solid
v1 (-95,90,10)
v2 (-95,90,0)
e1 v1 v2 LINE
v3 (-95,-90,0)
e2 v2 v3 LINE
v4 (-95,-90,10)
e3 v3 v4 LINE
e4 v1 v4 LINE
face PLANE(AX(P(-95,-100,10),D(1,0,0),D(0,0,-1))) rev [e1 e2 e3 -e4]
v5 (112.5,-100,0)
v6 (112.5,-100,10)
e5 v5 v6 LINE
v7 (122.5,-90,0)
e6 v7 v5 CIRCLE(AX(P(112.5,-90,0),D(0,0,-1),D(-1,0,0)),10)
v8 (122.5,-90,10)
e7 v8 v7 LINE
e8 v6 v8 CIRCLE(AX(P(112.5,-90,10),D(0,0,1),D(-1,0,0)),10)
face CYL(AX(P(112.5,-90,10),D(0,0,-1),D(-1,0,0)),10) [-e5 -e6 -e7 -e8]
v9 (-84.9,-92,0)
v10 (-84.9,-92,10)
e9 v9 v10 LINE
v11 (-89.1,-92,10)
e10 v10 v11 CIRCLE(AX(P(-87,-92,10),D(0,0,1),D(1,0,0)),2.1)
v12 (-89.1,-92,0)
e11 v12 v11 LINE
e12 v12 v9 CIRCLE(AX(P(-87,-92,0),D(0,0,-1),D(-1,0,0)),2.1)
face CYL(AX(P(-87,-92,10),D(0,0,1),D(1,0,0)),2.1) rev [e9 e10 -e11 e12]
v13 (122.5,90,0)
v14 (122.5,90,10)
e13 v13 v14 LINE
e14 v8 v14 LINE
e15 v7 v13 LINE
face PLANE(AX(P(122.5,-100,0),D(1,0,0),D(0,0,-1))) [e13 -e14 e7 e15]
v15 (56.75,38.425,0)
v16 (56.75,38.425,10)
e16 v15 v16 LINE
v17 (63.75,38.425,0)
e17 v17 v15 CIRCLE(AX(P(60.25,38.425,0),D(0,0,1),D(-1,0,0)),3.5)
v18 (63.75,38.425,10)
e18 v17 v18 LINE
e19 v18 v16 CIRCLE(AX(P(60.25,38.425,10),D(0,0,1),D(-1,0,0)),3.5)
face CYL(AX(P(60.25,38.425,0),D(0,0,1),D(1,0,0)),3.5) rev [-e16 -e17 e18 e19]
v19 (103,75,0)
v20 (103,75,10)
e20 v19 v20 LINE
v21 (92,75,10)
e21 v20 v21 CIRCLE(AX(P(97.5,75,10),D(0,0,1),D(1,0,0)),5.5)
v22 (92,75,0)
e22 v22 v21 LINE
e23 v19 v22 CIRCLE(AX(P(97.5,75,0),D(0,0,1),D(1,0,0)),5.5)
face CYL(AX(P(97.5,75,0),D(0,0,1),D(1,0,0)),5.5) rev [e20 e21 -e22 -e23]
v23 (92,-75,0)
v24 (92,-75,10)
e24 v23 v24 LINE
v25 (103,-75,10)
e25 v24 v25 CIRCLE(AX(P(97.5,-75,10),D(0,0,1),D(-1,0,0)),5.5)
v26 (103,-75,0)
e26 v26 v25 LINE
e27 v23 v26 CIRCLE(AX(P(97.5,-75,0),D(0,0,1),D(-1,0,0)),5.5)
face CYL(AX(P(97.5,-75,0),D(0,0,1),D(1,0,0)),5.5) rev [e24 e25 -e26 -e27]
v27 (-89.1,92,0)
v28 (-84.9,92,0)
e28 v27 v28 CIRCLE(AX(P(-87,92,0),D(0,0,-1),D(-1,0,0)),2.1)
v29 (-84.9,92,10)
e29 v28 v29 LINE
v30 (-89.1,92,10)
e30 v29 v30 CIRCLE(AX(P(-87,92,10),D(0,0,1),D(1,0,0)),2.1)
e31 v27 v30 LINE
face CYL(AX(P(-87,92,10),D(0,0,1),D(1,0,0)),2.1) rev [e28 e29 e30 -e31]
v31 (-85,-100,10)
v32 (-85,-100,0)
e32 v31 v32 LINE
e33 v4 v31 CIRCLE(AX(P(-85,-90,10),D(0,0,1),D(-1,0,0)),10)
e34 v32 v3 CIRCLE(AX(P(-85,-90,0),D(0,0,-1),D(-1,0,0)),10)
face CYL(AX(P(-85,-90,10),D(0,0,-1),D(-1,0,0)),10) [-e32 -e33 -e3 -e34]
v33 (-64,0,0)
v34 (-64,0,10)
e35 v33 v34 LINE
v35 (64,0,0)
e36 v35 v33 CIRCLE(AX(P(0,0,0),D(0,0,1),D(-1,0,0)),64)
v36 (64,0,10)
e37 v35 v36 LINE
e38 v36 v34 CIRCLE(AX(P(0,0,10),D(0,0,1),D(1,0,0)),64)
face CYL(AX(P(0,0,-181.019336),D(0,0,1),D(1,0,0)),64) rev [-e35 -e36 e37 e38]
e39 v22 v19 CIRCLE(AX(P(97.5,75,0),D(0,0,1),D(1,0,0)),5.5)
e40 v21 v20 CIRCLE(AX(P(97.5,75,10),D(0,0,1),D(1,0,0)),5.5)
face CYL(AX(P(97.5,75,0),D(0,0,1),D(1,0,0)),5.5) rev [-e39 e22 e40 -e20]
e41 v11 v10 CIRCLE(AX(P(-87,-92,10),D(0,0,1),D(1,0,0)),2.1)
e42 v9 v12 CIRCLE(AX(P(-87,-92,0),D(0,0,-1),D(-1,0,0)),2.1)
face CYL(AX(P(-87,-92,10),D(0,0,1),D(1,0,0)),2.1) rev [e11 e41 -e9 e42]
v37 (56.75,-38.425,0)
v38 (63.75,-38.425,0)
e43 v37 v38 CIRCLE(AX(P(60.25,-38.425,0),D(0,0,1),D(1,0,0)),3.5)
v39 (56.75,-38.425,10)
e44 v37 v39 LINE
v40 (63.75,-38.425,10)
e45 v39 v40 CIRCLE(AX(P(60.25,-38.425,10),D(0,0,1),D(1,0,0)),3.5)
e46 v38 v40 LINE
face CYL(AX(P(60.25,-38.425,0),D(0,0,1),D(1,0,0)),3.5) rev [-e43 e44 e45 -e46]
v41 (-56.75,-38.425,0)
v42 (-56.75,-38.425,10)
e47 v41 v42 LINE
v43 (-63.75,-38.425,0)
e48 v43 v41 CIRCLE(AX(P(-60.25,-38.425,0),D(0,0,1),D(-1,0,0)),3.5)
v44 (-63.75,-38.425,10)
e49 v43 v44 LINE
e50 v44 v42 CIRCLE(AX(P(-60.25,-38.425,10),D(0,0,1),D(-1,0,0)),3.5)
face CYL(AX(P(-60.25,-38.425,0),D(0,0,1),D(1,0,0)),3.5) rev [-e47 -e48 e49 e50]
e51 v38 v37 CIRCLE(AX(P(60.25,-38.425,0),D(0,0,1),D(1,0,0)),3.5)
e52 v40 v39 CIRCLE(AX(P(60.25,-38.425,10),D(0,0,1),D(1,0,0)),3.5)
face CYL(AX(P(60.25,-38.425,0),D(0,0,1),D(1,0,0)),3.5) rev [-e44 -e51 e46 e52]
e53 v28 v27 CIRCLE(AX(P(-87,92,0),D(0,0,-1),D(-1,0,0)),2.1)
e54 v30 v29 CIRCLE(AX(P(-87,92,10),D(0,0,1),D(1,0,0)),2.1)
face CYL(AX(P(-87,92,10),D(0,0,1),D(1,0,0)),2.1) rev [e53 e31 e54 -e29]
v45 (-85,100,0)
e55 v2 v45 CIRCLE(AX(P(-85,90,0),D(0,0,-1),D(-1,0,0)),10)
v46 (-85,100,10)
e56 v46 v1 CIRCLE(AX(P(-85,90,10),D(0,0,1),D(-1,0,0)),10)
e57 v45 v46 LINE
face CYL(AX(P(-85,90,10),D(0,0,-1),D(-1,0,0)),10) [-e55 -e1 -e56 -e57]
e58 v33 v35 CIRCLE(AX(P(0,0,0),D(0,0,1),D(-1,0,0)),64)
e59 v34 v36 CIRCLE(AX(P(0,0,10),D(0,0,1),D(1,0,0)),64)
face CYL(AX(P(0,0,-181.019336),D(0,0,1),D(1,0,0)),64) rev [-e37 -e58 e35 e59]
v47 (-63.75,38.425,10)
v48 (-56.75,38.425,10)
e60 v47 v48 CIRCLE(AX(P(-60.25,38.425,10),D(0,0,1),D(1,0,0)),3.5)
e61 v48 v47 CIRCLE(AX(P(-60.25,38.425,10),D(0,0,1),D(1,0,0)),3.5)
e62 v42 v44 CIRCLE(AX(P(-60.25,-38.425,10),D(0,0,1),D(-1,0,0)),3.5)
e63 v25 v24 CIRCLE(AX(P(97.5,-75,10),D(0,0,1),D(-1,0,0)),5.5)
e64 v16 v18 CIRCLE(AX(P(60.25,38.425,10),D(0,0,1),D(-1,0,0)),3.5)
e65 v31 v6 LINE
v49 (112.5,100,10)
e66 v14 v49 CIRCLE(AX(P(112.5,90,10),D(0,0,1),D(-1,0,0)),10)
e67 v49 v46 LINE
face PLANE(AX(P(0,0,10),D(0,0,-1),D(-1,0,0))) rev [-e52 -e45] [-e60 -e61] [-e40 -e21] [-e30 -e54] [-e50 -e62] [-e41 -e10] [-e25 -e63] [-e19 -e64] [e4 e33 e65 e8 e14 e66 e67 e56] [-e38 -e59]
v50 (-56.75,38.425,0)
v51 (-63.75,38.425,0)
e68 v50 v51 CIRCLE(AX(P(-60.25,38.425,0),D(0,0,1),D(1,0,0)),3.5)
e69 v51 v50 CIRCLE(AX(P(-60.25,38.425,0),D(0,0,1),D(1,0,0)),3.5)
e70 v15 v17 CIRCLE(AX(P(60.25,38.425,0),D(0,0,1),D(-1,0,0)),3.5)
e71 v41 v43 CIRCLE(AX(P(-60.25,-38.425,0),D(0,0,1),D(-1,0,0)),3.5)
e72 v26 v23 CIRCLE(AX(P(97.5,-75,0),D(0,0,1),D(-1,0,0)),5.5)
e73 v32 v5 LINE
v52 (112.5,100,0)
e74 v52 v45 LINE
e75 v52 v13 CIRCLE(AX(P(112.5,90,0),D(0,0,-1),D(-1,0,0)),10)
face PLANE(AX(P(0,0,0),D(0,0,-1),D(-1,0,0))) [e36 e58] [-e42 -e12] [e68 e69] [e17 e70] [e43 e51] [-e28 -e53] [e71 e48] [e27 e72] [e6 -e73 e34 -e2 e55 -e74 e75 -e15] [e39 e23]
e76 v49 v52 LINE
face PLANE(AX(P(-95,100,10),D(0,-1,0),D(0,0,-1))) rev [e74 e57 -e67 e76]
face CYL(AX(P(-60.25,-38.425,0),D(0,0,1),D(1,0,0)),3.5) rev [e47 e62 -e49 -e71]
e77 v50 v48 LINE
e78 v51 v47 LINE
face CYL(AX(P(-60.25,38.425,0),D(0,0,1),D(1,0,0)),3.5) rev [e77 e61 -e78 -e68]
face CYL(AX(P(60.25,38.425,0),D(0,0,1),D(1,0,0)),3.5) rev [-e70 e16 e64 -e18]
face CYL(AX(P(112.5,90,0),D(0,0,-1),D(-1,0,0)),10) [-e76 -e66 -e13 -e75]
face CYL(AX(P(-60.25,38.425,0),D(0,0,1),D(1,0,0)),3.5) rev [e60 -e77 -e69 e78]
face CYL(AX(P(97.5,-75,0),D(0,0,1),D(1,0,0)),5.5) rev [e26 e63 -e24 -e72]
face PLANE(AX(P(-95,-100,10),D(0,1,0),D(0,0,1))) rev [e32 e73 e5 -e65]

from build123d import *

# Parameters (mm, degrees)
SKETCH1_W             = 190
SKETCH1_H             = 200
BOSS_EXTRUDE1_DEPTH   = 10
SKETCH2_R             = 64
CUT_EXTRUDE1_DEPTH    = 10
SKETCH3_R             = 3.5
CUT_EXTRUDE2_DEPTH    = 10
SKETCH4_W             = 27.5
SKETCH4_H             = 200
BOSS_EXTRUDE2_DEPTH   = 10
SKETCH5_R             = 5.5
CUT_EXTRUDE3_DEPTH    = 10
SKETCH6_R             = 0.5
CUT_EXTRUDE4_DEPTH    = 10
M5_TAPPED_HOLE1_D     = 4.2
M5_TAPPED_HOLE1_DEPTH = 14
M5_TAPPED_HOLE1_TIP   = 1.2618073
FILLET1_R             = 10


with BuildPart() as part:
    # Sketch1 → Boss-Extrude1 (new body)
    with BuildSketch(Plane.XY):
        Rectangle(SKETCH1_W, SKETCH1_H)
    extrude(amount=BOSS_EXTRUDE1_DEPTH)

    # Sketch2 → Cut-Extrude1 (cut)
    with BuildSketch(Plane.XY.offset(10)):
        Circle(SKETCH2_R)
    extrude(amount=-CUT_EXTRUDE1_DEPTH, mode=Mode.SUBTRACT)

    # Sketch3 → Cut-Extrude2 (cut)
    with BuildSketch(Plane.XY.offset(10)):
        with Locations((-60.25, 38.425)):
            Circle(SKETCH3_R)
        with Locations(Location((60.25, 38.425, 0), (0, 0, 180))):
            Circle(SKETCH3_R)
        with Locations((60.25, -38.425)):
            Circle(SKETCH3_R)
        with Locations(Location((-60.25, -38.425, 0), (0, 0, 180))):
            Circle(SKETCH3_R)
    extrude(amount=-CUT_EXTRUDE2_DEPTH, mode=Mode.SUBTRACT)

    # Sketch4 → Boss-Extrude2 (add)
    with BuildSketch(Plane.XY.offset(10)):
        with Locations((108.75, 0)):
            Rectangle(SKETCH4_W, SKETCH4_H)
    extrude(amount=-BOSS_EXTRUDE2_DEPTH)

    # Sketch5 → Cut-Extrude3 (cut)
    with BuildSketch(Plane.XY.offset(10)):
        with Locations((97.5, 75)):
            Circle(SKETCH5_R)
        with Locations(Location((97.5, -75, 0), (0, 0, 180))):
            Circle(SKETCH5_R)
    extrude(amount=-CUT_EXTRUDE3_DEPTH, mode=Mode.SUBTRACT)

    # Sketch6 → Cut-Extrude4 (cut)
    with BuildSketch(Plane.XY.offset(10)):
        with Locations((-87, -92)):
            Circle(SKETCH6_R)
        with Locations(Location((-87, 92, 0), (0, 0, 180))):
            Circle(SKETCH6_R)
    extrude(amount=-CUT_EXTRUDE4_DEPTH, mode=Mode.SUBTRACT)

    # M5 Tapped Hole1
    with Locations(Plane.XY.offset(10)):
        with Locations((-87, 92), (-87, -92)):
            Hole(M5_TAPPED_HOLE1_D / 2, depth=M5_TAPPED_HOLE1_DEPTH)
            with Locations((0, 0, -(M5_TAPPED_HOLE1_DEPTH + M5_TAPPED_HOLE1_TIP / 2))):  # 118° drill point
                Cone(0, M5_TAPPED_HOLE1_D / 2, M5_TAPPED_HOLE1_TIP, mode=Mode.SUBTRACT)

    # Fillet1
    fillet1_edges = [part.edges().sort_by_distance(p)[0] for p in [
        (122.5, 100, 5),
        (122.5, -100, 5),
        (-95, -100, 5),
        (-95, 100, 5),
    ]]
    fillet(fillet1_edges, radius=FILLET1_R)


solid = part.part
